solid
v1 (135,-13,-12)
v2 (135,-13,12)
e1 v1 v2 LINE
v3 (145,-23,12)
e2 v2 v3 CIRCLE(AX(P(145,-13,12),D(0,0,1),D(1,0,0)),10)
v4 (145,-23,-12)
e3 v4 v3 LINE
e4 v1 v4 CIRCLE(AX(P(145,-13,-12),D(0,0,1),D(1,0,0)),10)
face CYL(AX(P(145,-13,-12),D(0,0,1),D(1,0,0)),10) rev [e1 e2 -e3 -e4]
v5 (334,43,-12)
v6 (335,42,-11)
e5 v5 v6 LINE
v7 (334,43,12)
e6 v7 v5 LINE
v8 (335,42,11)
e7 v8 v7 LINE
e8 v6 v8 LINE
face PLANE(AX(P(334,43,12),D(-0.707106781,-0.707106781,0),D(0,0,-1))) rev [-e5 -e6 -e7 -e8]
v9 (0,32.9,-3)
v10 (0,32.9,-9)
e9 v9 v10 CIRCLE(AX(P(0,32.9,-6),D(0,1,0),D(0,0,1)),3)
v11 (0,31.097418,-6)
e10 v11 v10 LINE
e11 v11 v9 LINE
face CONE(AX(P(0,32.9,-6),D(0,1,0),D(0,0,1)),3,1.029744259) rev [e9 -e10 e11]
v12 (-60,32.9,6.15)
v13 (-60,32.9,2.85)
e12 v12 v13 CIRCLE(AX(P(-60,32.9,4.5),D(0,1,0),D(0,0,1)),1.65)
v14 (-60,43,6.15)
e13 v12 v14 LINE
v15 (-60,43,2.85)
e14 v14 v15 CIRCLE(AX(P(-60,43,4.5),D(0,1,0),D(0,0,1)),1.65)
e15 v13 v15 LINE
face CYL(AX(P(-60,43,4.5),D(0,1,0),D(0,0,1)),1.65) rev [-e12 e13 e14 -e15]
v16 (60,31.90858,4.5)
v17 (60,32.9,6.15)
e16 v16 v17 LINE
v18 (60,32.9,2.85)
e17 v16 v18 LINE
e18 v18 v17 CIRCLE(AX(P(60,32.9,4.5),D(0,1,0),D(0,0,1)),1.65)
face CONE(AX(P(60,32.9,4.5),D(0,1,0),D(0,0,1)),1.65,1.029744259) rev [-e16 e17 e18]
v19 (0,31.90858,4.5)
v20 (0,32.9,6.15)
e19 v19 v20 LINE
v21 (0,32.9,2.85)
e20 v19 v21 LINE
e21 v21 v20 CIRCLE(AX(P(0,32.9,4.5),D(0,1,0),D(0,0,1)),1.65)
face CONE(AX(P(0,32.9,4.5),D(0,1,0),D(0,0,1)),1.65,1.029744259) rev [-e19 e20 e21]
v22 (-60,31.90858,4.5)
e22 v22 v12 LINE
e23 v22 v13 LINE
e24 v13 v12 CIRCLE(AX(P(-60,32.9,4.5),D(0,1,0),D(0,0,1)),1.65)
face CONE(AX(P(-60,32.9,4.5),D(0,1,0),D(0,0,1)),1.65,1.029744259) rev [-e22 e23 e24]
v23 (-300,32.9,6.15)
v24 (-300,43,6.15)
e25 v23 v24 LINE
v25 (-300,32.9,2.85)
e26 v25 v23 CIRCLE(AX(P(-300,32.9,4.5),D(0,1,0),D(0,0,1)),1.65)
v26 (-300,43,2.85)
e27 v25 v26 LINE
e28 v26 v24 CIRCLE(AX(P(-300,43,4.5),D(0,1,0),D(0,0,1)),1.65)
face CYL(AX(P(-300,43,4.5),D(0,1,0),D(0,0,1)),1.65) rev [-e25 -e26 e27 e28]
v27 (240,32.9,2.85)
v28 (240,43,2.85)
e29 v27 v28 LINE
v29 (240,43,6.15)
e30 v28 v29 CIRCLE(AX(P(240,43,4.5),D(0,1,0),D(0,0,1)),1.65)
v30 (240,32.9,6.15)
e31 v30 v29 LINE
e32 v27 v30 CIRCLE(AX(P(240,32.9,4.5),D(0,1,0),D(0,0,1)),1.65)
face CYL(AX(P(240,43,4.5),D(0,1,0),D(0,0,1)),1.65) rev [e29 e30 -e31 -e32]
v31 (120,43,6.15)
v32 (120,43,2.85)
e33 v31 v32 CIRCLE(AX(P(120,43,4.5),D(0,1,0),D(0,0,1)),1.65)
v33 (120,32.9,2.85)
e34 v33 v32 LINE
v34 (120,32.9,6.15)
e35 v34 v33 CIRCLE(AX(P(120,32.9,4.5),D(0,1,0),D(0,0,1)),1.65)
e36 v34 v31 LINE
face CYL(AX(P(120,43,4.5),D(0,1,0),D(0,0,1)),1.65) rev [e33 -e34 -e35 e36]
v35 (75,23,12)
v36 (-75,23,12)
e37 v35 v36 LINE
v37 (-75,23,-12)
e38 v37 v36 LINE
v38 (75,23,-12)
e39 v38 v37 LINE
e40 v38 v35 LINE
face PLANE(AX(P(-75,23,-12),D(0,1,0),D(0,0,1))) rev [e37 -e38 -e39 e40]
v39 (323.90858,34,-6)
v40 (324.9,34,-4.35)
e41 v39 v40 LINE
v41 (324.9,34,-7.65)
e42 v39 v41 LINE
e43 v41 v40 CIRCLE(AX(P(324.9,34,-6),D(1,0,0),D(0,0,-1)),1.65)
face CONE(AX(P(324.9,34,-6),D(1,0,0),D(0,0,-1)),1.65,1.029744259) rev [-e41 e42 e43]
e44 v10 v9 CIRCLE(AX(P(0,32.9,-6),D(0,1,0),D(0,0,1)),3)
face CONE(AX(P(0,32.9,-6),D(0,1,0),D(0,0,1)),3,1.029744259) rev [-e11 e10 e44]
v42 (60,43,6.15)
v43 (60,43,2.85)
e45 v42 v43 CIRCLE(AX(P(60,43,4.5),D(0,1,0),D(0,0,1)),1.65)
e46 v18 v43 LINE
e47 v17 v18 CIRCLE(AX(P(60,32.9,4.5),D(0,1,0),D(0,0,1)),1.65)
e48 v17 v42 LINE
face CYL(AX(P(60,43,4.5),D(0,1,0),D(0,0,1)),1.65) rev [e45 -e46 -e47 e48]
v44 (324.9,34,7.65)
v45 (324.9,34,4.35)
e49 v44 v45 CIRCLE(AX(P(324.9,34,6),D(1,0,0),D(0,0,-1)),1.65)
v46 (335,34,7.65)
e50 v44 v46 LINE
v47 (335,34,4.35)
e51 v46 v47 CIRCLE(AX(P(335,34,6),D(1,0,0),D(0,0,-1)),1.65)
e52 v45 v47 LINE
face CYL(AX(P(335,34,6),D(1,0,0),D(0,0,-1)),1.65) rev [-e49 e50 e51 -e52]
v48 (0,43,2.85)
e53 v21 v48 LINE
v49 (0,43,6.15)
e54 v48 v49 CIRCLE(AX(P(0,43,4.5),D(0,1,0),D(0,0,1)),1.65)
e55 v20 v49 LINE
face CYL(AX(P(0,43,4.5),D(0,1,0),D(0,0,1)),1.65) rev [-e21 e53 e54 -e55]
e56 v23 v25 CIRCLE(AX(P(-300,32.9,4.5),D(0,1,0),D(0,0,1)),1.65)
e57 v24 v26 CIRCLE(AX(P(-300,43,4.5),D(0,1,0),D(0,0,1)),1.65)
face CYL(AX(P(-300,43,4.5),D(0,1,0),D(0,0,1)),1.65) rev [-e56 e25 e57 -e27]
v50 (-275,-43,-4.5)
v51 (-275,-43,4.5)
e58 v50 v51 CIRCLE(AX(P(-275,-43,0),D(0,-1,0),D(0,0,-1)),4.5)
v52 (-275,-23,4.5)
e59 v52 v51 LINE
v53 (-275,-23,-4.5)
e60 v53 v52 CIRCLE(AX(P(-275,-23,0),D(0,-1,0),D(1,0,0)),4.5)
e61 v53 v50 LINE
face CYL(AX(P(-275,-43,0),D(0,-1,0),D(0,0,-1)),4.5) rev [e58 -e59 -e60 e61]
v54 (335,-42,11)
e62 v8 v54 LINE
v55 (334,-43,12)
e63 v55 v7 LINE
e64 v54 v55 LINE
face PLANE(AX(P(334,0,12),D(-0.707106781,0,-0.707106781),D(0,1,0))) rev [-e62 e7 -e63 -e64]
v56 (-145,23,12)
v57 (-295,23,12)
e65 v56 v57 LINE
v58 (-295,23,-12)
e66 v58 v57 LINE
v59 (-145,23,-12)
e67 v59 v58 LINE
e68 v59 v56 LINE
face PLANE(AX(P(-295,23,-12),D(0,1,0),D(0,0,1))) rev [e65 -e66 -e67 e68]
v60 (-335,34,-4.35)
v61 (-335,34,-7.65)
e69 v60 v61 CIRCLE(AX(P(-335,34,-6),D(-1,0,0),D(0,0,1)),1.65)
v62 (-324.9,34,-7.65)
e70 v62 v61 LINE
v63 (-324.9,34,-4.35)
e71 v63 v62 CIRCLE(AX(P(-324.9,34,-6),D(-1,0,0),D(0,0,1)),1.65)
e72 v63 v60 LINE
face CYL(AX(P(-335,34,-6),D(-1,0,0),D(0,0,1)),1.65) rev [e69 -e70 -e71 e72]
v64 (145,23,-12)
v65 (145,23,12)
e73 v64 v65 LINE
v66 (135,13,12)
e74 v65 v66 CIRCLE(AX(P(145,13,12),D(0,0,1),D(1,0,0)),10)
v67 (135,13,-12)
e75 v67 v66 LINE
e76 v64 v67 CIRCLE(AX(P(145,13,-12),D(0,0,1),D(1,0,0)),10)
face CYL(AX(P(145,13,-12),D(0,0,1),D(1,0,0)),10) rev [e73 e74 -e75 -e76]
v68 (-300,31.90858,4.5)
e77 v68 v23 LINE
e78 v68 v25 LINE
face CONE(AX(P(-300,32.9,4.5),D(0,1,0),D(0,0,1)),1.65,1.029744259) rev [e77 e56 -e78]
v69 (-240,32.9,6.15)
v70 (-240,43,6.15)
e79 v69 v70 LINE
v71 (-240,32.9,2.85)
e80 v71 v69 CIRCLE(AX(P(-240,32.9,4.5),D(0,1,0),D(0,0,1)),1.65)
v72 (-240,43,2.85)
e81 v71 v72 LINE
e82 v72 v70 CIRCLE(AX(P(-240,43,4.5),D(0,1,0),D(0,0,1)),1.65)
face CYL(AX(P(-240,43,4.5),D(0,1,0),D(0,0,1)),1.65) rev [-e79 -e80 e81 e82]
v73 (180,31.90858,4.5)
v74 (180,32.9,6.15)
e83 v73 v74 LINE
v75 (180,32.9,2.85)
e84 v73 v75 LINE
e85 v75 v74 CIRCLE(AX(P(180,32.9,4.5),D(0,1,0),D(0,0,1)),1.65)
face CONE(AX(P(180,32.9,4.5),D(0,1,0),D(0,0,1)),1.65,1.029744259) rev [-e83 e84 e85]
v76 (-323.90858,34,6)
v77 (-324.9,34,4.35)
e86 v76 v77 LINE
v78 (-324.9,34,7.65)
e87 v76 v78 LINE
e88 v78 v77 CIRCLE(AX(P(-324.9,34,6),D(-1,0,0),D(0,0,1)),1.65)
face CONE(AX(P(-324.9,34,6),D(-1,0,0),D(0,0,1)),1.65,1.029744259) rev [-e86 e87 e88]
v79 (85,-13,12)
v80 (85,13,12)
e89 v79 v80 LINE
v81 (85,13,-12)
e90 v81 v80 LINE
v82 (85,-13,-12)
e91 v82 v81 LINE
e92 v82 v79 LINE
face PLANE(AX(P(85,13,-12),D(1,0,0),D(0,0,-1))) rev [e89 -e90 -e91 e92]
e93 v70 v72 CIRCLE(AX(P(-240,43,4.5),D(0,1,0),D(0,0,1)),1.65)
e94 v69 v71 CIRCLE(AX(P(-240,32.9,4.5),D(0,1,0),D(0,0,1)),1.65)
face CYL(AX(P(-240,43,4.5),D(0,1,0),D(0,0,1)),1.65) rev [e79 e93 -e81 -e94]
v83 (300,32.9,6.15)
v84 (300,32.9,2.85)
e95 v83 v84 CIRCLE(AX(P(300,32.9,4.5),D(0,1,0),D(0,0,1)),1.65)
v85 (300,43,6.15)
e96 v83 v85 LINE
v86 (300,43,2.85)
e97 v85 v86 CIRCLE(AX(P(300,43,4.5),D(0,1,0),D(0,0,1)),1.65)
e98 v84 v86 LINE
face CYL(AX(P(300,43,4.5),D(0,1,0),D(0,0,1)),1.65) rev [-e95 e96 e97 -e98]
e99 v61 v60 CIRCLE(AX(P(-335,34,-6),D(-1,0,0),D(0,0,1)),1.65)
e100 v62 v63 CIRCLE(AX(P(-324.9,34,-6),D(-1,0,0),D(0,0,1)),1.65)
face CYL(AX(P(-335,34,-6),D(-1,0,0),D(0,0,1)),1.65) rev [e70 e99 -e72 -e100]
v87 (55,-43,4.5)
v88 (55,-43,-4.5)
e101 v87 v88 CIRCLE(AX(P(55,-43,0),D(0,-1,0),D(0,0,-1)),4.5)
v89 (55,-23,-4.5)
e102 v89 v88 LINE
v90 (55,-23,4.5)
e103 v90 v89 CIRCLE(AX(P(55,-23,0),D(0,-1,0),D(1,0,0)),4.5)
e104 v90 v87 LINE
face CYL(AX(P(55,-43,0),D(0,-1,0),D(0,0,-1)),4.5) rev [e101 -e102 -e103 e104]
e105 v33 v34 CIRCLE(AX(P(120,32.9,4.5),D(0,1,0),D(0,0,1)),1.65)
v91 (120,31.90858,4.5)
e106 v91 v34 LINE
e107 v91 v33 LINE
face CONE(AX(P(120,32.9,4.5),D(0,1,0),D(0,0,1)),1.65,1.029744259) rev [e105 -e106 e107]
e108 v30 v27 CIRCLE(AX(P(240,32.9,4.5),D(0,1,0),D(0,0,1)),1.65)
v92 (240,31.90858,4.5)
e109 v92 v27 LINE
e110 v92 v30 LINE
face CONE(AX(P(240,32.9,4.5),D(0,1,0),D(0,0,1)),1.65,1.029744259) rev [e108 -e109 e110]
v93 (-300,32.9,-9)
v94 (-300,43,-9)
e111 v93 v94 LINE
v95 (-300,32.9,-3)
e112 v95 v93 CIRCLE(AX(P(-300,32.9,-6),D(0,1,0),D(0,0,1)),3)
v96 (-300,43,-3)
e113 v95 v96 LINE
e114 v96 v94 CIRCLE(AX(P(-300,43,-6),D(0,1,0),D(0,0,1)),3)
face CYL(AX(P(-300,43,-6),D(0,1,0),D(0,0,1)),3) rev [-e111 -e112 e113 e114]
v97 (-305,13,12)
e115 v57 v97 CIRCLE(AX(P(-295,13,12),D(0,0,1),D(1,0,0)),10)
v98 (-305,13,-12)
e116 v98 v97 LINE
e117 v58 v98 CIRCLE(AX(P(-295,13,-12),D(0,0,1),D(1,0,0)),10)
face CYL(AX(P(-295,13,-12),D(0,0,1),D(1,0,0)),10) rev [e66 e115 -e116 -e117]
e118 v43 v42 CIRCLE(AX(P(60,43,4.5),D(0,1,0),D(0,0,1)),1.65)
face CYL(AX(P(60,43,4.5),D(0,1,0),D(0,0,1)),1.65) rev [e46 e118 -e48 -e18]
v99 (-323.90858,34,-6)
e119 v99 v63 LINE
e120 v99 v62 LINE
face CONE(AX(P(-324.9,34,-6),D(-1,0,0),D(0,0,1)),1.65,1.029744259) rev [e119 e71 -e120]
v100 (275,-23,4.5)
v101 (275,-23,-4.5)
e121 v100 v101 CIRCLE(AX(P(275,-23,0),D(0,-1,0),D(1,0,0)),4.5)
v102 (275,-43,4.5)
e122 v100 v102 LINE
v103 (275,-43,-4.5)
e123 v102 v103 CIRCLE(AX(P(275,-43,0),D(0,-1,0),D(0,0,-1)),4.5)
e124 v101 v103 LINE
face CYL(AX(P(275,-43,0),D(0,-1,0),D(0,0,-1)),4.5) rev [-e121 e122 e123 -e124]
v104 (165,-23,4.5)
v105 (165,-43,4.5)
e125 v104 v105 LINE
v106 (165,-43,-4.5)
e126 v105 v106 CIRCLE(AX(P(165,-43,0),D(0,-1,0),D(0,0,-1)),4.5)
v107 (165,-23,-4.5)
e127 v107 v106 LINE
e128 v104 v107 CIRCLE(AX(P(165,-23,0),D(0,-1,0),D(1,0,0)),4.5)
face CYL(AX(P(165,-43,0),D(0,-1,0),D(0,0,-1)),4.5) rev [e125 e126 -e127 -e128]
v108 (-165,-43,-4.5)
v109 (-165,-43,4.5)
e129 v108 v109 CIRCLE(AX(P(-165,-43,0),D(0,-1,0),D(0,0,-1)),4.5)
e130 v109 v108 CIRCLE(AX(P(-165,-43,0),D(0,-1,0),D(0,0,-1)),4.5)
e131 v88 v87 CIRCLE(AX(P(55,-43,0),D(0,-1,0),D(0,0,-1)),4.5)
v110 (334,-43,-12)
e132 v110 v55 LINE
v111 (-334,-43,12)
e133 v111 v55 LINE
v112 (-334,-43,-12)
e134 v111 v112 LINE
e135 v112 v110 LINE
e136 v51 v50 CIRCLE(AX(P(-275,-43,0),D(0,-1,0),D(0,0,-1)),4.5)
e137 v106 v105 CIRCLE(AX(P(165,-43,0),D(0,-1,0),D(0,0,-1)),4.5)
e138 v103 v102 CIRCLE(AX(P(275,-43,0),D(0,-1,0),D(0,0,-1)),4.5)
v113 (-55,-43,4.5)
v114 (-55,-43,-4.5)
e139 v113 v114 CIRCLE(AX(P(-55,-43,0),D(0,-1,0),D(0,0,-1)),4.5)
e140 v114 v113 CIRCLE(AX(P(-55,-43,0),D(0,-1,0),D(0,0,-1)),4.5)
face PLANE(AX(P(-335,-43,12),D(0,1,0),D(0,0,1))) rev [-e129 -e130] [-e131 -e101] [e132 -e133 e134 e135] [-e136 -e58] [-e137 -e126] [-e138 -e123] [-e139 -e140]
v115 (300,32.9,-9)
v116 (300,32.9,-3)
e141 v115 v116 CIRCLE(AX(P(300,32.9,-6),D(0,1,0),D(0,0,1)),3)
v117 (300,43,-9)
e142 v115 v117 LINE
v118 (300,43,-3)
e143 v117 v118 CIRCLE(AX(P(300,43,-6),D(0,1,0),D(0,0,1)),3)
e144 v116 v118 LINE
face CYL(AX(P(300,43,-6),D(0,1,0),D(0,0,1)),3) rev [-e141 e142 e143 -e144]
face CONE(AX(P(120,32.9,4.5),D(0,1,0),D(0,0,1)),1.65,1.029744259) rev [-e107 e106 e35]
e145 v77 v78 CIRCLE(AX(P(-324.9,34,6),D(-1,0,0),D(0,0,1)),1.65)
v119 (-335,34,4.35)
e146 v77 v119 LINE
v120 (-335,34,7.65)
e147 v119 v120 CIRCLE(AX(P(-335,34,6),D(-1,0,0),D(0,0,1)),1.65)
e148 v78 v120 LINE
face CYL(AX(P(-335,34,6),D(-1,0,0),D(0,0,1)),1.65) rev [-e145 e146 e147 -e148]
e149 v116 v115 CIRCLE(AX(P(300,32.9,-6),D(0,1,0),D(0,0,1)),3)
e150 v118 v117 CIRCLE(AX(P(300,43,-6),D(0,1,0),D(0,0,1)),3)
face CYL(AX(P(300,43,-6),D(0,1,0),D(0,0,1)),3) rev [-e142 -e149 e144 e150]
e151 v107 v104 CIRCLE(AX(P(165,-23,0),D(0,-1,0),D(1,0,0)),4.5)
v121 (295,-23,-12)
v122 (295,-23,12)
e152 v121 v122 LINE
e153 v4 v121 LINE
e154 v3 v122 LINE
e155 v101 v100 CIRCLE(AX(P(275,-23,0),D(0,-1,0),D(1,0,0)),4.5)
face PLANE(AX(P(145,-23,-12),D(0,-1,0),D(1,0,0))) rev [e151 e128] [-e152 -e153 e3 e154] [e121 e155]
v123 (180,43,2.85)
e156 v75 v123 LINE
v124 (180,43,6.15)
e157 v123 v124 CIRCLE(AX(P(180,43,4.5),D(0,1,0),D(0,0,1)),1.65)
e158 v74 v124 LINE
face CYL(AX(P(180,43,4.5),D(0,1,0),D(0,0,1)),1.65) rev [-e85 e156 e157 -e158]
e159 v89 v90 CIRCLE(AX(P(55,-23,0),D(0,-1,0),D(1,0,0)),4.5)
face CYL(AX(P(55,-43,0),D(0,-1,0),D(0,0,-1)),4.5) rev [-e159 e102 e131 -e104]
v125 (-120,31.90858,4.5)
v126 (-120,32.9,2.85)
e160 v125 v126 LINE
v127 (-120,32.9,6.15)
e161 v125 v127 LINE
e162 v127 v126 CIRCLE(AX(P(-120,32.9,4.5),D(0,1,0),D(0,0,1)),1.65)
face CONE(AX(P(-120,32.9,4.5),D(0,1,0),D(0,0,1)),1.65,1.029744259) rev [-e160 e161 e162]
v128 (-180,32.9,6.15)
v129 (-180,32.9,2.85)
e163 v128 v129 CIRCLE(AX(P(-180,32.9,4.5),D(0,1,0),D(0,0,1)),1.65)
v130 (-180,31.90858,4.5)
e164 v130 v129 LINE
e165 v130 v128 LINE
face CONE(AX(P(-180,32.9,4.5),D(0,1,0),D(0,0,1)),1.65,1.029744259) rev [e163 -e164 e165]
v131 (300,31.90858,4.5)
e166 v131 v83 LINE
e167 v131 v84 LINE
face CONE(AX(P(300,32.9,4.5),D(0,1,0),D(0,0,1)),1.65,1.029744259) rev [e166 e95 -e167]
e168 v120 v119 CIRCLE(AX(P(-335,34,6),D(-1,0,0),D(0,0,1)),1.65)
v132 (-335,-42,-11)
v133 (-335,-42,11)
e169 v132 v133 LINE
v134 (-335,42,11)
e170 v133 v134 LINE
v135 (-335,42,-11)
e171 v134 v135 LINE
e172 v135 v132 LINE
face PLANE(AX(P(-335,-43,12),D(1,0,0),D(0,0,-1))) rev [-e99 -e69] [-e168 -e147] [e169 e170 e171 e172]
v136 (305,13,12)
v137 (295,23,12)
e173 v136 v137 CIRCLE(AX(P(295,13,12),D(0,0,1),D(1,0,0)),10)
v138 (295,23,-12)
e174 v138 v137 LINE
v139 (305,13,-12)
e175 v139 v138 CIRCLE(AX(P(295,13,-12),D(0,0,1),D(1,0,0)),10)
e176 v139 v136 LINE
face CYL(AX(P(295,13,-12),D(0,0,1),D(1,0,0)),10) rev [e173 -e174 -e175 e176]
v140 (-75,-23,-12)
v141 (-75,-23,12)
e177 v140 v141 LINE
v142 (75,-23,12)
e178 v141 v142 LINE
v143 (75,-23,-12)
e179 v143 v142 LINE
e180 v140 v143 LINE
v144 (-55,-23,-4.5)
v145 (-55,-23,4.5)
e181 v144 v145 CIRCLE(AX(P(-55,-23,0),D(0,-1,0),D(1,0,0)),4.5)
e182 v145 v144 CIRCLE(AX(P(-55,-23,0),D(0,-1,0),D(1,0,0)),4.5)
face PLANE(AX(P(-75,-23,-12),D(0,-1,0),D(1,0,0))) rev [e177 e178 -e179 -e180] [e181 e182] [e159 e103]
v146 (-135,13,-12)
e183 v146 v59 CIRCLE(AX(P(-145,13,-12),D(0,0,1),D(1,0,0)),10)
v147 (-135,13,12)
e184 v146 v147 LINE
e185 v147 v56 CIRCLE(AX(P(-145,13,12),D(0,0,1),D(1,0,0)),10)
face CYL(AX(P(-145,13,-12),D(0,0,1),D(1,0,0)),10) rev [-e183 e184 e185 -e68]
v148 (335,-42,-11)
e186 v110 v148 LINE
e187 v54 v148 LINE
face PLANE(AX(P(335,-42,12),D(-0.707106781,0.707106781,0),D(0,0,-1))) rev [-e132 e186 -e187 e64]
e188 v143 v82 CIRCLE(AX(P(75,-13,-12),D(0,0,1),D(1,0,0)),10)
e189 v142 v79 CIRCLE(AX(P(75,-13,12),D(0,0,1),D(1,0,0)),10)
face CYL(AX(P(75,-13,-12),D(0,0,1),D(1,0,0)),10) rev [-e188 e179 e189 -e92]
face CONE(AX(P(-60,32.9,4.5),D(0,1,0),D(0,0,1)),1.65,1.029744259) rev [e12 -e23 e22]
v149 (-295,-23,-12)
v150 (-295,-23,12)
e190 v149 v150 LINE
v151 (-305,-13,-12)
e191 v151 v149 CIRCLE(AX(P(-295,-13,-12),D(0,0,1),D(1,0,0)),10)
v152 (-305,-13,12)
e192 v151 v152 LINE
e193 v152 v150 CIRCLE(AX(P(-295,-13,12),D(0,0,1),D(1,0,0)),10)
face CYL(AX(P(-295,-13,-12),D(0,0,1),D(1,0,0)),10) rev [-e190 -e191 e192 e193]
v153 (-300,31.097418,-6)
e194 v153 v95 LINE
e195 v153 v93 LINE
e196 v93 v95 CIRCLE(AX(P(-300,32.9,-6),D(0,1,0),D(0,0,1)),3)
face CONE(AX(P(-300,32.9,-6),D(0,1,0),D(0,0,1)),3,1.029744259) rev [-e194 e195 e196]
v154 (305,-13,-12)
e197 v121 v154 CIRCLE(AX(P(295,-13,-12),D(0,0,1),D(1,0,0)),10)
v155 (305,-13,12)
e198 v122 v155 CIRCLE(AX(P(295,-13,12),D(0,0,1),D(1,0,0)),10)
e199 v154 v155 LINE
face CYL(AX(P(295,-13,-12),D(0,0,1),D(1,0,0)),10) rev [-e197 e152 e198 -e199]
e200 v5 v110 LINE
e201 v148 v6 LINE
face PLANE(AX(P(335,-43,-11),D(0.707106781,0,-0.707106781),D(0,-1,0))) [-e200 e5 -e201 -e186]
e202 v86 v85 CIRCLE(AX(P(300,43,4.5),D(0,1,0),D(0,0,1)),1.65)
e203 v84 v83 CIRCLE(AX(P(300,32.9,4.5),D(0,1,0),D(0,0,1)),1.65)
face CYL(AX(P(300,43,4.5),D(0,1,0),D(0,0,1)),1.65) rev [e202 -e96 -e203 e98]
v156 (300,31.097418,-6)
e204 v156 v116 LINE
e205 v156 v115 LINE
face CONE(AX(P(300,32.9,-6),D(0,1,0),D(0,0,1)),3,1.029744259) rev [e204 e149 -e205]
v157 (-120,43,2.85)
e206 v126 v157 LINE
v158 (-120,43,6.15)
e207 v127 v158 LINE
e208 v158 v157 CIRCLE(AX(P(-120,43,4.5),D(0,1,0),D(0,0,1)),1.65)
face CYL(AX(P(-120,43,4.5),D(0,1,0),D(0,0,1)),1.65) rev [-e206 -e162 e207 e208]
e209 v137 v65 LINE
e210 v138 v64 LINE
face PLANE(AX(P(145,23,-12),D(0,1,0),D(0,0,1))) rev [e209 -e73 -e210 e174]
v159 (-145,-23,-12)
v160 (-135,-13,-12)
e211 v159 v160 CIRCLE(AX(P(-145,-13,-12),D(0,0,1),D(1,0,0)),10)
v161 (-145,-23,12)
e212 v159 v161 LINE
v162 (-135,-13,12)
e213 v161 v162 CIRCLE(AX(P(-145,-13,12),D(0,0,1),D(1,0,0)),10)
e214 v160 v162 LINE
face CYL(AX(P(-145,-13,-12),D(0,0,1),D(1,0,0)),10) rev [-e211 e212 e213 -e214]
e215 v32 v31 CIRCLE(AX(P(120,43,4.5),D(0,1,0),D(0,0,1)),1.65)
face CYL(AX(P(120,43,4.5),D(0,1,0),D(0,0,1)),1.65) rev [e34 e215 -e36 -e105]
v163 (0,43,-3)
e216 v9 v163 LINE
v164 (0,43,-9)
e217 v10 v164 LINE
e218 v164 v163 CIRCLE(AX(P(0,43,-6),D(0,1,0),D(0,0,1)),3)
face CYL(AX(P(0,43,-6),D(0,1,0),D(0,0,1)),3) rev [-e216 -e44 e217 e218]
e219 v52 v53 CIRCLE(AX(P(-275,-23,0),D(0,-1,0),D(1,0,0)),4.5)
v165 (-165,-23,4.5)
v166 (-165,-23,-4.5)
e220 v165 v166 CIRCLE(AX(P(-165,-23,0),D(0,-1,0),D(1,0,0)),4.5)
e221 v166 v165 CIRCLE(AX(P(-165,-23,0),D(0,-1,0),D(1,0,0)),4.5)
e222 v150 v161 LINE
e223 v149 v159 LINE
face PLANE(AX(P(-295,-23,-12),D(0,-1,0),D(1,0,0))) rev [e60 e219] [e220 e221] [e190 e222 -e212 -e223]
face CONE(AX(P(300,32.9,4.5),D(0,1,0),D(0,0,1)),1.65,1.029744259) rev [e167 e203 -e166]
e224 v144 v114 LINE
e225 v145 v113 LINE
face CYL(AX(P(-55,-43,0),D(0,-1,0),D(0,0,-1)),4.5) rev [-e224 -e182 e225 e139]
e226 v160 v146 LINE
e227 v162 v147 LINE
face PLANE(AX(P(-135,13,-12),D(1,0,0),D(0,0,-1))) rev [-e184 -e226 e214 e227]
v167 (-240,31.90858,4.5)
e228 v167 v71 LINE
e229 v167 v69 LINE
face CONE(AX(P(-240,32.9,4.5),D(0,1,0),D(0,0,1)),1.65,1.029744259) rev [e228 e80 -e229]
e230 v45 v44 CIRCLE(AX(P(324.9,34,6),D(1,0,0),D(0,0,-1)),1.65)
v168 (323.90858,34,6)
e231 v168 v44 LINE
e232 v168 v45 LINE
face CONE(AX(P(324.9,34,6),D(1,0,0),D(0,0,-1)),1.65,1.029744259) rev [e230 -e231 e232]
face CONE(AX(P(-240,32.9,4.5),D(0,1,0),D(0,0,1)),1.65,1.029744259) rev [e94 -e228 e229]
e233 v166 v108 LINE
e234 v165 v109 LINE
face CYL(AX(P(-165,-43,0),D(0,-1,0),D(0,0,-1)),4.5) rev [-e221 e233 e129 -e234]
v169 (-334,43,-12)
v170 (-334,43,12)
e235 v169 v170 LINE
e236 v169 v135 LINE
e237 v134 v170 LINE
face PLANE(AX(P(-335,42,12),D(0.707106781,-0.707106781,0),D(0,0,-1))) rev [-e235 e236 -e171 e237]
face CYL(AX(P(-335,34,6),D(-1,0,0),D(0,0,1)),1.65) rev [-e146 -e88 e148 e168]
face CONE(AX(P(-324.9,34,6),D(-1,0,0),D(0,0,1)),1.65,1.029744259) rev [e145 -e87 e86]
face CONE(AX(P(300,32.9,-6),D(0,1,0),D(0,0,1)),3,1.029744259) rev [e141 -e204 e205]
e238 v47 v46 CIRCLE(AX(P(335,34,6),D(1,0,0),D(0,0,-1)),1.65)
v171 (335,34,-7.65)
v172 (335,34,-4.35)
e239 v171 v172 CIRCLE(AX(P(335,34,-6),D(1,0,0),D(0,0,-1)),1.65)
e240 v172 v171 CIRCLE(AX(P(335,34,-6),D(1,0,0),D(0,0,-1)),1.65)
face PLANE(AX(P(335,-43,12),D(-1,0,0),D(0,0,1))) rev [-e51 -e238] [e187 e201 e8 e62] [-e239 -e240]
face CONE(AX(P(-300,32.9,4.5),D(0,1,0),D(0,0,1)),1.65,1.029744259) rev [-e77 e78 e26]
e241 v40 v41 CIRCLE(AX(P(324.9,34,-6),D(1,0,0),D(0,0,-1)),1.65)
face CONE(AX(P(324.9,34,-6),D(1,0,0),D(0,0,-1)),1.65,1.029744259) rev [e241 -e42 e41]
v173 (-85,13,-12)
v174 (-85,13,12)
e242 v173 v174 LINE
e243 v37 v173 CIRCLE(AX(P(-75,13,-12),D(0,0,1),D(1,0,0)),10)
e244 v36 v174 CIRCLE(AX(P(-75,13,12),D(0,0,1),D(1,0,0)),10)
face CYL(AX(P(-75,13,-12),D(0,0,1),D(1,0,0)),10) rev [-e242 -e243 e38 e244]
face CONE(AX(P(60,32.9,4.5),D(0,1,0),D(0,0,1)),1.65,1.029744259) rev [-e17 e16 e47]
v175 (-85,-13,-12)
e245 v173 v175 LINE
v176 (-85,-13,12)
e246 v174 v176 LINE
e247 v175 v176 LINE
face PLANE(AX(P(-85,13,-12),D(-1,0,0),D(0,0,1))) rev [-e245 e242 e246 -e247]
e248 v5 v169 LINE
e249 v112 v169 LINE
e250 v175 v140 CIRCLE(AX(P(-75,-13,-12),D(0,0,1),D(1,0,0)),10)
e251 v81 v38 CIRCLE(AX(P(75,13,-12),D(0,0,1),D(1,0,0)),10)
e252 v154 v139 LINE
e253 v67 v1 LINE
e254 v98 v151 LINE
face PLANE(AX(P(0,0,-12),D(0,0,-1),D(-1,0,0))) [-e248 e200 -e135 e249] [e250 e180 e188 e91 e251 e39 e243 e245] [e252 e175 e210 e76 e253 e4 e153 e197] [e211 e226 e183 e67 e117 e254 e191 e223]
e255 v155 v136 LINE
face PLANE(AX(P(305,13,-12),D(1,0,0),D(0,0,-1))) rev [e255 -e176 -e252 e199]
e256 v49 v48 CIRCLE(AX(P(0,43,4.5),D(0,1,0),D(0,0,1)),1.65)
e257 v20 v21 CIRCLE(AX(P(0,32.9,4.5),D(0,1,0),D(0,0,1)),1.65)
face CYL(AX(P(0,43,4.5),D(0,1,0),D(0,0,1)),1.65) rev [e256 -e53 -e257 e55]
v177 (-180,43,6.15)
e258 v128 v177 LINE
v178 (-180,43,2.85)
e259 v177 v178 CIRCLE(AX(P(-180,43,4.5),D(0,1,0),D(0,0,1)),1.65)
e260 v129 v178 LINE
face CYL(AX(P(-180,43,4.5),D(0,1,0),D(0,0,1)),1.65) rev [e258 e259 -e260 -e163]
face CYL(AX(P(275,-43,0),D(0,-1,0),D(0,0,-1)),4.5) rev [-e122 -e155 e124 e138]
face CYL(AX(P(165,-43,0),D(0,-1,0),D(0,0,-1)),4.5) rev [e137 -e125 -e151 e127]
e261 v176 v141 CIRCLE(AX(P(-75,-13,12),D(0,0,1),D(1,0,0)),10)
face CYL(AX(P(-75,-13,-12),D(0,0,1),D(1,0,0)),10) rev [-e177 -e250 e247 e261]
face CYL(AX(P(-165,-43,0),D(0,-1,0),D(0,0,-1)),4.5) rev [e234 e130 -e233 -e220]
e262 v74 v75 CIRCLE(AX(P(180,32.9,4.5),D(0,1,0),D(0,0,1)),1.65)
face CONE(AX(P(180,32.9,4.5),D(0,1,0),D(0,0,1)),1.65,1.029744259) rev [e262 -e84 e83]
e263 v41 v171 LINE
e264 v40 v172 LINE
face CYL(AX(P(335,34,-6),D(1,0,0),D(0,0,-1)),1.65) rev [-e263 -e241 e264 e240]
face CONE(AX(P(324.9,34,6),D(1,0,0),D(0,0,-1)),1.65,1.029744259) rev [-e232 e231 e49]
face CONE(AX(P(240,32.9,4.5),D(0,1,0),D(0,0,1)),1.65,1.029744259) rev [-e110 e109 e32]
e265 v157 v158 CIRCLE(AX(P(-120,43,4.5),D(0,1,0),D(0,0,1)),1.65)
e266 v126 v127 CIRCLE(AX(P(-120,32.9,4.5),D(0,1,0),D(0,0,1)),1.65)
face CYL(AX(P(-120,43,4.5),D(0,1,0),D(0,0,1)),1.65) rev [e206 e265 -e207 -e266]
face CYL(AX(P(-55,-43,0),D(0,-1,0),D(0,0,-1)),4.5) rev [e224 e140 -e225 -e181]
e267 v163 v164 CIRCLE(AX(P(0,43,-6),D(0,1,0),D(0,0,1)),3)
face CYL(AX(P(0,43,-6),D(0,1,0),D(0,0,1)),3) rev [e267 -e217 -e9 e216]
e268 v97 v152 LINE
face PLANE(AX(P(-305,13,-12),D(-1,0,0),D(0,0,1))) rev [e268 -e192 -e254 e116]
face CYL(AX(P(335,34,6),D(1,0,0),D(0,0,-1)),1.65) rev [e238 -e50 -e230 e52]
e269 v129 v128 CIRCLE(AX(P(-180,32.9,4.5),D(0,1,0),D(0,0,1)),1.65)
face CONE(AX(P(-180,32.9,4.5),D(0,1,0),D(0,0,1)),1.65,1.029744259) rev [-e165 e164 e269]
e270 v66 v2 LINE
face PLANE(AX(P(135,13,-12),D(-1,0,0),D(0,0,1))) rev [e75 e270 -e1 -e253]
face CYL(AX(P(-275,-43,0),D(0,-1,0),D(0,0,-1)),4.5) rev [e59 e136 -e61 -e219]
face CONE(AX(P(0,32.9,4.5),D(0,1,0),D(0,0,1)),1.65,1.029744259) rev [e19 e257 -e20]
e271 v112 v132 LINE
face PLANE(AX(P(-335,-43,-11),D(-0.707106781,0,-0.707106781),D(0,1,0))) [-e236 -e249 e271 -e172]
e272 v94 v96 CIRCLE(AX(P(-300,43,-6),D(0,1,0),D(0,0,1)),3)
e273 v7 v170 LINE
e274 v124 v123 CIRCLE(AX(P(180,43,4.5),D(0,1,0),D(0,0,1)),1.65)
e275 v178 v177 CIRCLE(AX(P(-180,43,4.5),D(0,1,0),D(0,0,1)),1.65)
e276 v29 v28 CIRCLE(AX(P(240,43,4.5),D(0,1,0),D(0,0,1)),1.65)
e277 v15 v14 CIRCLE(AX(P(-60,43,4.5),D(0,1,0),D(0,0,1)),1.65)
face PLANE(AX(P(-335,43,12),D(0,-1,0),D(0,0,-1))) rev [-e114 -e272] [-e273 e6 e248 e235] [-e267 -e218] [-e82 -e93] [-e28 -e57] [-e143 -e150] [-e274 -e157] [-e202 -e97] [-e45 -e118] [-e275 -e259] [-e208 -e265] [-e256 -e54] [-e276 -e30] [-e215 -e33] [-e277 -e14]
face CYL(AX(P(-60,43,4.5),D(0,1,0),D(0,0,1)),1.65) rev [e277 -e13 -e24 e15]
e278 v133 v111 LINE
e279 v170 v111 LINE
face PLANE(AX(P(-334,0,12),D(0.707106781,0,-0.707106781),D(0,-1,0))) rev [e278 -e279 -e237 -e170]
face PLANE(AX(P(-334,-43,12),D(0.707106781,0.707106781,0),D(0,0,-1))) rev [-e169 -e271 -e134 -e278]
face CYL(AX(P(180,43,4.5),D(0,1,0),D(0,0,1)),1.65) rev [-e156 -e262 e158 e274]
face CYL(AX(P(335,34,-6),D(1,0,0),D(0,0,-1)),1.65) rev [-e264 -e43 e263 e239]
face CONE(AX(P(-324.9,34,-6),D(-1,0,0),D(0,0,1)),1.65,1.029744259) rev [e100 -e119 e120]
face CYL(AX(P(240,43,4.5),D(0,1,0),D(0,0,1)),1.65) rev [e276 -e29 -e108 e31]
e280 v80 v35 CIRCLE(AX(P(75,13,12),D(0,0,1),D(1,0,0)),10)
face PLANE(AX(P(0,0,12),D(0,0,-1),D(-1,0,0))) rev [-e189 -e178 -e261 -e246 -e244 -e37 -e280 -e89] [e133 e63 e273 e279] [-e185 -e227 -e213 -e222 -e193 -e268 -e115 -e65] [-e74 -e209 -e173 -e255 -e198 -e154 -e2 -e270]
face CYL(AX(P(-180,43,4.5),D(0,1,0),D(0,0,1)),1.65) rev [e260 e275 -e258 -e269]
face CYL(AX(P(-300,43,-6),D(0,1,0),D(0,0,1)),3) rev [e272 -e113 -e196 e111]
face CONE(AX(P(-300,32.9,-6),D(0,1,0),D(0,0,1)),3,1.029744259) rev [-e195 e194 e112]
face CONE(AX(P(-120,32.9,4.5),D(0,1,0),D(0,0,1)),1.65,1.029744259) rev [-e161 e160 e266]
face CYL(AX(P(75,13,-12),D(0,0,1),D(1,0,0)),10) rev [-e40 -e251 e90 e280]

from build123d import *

# Parameters (mm, degrees)
SKETCH1_W                = 670
SKETCH1_H                = 86
BOSS_EXTRUDE1_DEPTH      = 12
CUT_EXTRUDE1_DEPTH       = 339.600059067
M8_CLEARANCE_HOLE1_D     = 9
M8_CLEARANCE_HOLE1_DEPTH = 20
M4_TAPPED_HOLE1_D        = 3.3
M4_TAPPED_HOLE1_DEPTH    = 10.1
M4_TAPPED_HOLE1_TIP      = 0.991420021
DOWEL_HOLE1_D            = 6
DOWEL_HOLE1_DEPTH        = 10.1
DOWEL_HOLE1_TIP          = 1.802581857
CHAMFER1_SIZE            = 1
M4_TAPPED_HOLE2_D        = 3.3
M4_TAPPED_HOLE2_DEPTH    = 10.1
M4_TAPPED_HOLE2_TIP      = 0.991420021
M4_TAPPED_HOLE3_D        = 3.3
M4_TAPPED_HOLE3_DEPTH    = 10.1
M4_TAPPED_HOLE3_TIP      = 0.991420021


with BuildPart() as part:
    # Sketch1 → Boss-Extrude1 (new, symmetric)
    with BuildSketch(Plane.XY):
        Rectangle(SKETCH1_W, SKETCH1_H)
    extrude(amount=BOSS_EXTRUDE1_DEPTH, both=True)

    # Sketch2 → Cut-Extrude1 (cut, through all)
    with BuildSketch(Plane.XY.offset(12)):
        with BuildLine():
            Line((-295, 23), (-145, 23))
            ThreePointArc((-145, 23), (-137.928932188, 20.071067812), (-135, 13))
            Line((-135, 13), (-135, -13))
            ThreePointArc((-135, -13), (-137.928932188, -20.071067812), (-145, -23))
            Line((-145, -23), (-295, -23))
            ThreePointArc((-295, -23), (-302.071067812, -20.071067812), (-305, -13))
            Line((-305, -13), (-305, 13))
            ThreePointArc((-305, 13), (-302.071067812, 20.071067812), (-295, 23))
        make_face()
        with BuildLine():
            Line((-75, 23), (75, 23))
            ThreePointArc((75, 23), (82.071067812, 20.071067812), (85, 13))
            Line((85, 13), (85, -13))
            ThreePointArc((85, -13), (82.071067812, -20.071067812), (75, -23))
            Line((75, -23), (-75, -23))
            ThreePointArc((-75, -23), (-82.071067812, -20.071067812), (-85, -13))
            Line((-85, -13), (-85, 13))
            ThreePointArc((-85, 13), (-82.071067812, 20.071067812), (-75, 23))
        make_face()
        with BuildLine():
            Line((145, 23), (295, 23))
            ThreePointArc((295, 23), (302.071067812, 20.071067812), (305, 13))
            Line((305, 13), (305, -13))
            ThreePointArc((305, -13), (302.071067812, -20.071067812), (295, -23))
            Line((295, -23), (145, -23))
            ThreePointArc((145, -23), (137.928932188, -20.071067812), (135, -13))
            Line((135, -13), (135, 13))
            ThreePointArc((135, 13), (137.928932188, 20.071067812), (145, 23))
        make_face()
    extrude(amount=-CUT_EXTRUDE1_DEPTH, mode=Mode.SUBTRACT)

    # M8 Clearance Hole1
    with Locations(Plane(origin=(0, -43, 0), x_dir=(-1, 0, 0), z_dir=(0, -1, 0))):
        with Locations((-275, 0), (275, 0), (165, 0), (55, 0), (-55, 0), (-165, 0)):
            Hole(M8_CLEARANCE_HOLE1_D / 2, depth=M8_CLEARANCE_HOLE1_DEPTH)

    # M4 Tapped Hole1
    with Locations(Plane(origin=(0, 43, 0), x_dir=(1, 0, 0), z_dir=(0, 1, 0))):
        with Locations((-300, -4.5), (-240, -4.5), (-180, -4.5), (-120, -4.5), (-60, -4.5), (0, -4.5), (60, -4.5), (120, -4.5), (180, -4.5), (240, -4.5), (300, -4.5)):
            Hole(M4_TAPPED_HOLE1_D / 2, depth=M4_TAPPED_HOLE1_DEPTH)
            with Locations((0, 0, -(M4_TAPPED_HOLE1_DEPTH + M4_TAPPED_HOLE1_TIP / 2))):  # 118° drill point
                Cone(0, M4_TAPPED_HOLE1_D / 2, M4_TAPPED_HOLE1_TIP, mode=Mode.SUBTRACT)

    # Dowel Hole1
    with Locations(Plane(origin=(0, 43, 0), x_dir=(1, 0, 0), z_dir=(0, 1, 0))):
        with Locations((300, 6), (-300, 6), (0, 6)):
            Hole(DOWEL_HOLE1_D / 2, depth=DOWEL_HOLE1_DEPTH)
            with Locations((0, 0, -(DOWEL_HOLE1_DEPTH + DOWEL_HOLE1_TIP / 2))):  # 118° drill point
                Cone(0, DOWEL_HOLE1_D / 2, DOWEL_HOLE1_TIP, mode=Mode.SUBTRACT)

    # Chamfer1
    chamfer1_edges = [part.edges().sort_by_distance(p)[0] for p in [
        (-335, 0, 12),
        (335, 0, 12),
        (-335, 0, -12),
        (335, 0, -12),
        (335, -43, 0),
        (-335, -43, 0),
        (-335, 43, 0),
        (335, 43, 0),
    ]]
    chamfer(chamfer1_edges, length=CHAMFER1_SIZE)

    # M4 Tapped Hole2
    with Locations(Plane.ZY.offset(335)):
        with Locations((6, 34), (-6, 34)):
            Hole(M4_TAPPED_HOLE2_D / 2, depth=M4_TAPPED_HOLE2_DEPTH)
            with Locations((0, 0, -(M4_TAPPED_HOLE2_DEPTH + M4_TAPPED_HOLE2_TIP / 2))):  # 118° drill point
                Cone(0, M4_TAPPED_HOLE2_D / 2, M4_TAPPED_HOLE2_TIP, mode=Mode.SUBTRACT)

    # M4 Tapped Hole3
    with Locations(Plane(origin=(335, 0, 0), x_dir=(0, 0, -1), z_dir=(1, 0, 0))):
        with Locations((-6, 34), (6, 34)):
            Hole(M4_TAPPED_HOLE3_D / 2, depth=M4_TAPPED_HOLE3_DEPTH)
            with Locations((0, 0, -(M4_TAPPED_HOLE3_DEPTH + M4_TAPPED_HOLE3_TIP / 2))):  # 118° drill point
                Cone(0, M4_TAPPED_HOLE3_D / 2, M4_TAPPED_HOLE3_TIP, mode=Mode.SUBTRACT)


solid = part.part
